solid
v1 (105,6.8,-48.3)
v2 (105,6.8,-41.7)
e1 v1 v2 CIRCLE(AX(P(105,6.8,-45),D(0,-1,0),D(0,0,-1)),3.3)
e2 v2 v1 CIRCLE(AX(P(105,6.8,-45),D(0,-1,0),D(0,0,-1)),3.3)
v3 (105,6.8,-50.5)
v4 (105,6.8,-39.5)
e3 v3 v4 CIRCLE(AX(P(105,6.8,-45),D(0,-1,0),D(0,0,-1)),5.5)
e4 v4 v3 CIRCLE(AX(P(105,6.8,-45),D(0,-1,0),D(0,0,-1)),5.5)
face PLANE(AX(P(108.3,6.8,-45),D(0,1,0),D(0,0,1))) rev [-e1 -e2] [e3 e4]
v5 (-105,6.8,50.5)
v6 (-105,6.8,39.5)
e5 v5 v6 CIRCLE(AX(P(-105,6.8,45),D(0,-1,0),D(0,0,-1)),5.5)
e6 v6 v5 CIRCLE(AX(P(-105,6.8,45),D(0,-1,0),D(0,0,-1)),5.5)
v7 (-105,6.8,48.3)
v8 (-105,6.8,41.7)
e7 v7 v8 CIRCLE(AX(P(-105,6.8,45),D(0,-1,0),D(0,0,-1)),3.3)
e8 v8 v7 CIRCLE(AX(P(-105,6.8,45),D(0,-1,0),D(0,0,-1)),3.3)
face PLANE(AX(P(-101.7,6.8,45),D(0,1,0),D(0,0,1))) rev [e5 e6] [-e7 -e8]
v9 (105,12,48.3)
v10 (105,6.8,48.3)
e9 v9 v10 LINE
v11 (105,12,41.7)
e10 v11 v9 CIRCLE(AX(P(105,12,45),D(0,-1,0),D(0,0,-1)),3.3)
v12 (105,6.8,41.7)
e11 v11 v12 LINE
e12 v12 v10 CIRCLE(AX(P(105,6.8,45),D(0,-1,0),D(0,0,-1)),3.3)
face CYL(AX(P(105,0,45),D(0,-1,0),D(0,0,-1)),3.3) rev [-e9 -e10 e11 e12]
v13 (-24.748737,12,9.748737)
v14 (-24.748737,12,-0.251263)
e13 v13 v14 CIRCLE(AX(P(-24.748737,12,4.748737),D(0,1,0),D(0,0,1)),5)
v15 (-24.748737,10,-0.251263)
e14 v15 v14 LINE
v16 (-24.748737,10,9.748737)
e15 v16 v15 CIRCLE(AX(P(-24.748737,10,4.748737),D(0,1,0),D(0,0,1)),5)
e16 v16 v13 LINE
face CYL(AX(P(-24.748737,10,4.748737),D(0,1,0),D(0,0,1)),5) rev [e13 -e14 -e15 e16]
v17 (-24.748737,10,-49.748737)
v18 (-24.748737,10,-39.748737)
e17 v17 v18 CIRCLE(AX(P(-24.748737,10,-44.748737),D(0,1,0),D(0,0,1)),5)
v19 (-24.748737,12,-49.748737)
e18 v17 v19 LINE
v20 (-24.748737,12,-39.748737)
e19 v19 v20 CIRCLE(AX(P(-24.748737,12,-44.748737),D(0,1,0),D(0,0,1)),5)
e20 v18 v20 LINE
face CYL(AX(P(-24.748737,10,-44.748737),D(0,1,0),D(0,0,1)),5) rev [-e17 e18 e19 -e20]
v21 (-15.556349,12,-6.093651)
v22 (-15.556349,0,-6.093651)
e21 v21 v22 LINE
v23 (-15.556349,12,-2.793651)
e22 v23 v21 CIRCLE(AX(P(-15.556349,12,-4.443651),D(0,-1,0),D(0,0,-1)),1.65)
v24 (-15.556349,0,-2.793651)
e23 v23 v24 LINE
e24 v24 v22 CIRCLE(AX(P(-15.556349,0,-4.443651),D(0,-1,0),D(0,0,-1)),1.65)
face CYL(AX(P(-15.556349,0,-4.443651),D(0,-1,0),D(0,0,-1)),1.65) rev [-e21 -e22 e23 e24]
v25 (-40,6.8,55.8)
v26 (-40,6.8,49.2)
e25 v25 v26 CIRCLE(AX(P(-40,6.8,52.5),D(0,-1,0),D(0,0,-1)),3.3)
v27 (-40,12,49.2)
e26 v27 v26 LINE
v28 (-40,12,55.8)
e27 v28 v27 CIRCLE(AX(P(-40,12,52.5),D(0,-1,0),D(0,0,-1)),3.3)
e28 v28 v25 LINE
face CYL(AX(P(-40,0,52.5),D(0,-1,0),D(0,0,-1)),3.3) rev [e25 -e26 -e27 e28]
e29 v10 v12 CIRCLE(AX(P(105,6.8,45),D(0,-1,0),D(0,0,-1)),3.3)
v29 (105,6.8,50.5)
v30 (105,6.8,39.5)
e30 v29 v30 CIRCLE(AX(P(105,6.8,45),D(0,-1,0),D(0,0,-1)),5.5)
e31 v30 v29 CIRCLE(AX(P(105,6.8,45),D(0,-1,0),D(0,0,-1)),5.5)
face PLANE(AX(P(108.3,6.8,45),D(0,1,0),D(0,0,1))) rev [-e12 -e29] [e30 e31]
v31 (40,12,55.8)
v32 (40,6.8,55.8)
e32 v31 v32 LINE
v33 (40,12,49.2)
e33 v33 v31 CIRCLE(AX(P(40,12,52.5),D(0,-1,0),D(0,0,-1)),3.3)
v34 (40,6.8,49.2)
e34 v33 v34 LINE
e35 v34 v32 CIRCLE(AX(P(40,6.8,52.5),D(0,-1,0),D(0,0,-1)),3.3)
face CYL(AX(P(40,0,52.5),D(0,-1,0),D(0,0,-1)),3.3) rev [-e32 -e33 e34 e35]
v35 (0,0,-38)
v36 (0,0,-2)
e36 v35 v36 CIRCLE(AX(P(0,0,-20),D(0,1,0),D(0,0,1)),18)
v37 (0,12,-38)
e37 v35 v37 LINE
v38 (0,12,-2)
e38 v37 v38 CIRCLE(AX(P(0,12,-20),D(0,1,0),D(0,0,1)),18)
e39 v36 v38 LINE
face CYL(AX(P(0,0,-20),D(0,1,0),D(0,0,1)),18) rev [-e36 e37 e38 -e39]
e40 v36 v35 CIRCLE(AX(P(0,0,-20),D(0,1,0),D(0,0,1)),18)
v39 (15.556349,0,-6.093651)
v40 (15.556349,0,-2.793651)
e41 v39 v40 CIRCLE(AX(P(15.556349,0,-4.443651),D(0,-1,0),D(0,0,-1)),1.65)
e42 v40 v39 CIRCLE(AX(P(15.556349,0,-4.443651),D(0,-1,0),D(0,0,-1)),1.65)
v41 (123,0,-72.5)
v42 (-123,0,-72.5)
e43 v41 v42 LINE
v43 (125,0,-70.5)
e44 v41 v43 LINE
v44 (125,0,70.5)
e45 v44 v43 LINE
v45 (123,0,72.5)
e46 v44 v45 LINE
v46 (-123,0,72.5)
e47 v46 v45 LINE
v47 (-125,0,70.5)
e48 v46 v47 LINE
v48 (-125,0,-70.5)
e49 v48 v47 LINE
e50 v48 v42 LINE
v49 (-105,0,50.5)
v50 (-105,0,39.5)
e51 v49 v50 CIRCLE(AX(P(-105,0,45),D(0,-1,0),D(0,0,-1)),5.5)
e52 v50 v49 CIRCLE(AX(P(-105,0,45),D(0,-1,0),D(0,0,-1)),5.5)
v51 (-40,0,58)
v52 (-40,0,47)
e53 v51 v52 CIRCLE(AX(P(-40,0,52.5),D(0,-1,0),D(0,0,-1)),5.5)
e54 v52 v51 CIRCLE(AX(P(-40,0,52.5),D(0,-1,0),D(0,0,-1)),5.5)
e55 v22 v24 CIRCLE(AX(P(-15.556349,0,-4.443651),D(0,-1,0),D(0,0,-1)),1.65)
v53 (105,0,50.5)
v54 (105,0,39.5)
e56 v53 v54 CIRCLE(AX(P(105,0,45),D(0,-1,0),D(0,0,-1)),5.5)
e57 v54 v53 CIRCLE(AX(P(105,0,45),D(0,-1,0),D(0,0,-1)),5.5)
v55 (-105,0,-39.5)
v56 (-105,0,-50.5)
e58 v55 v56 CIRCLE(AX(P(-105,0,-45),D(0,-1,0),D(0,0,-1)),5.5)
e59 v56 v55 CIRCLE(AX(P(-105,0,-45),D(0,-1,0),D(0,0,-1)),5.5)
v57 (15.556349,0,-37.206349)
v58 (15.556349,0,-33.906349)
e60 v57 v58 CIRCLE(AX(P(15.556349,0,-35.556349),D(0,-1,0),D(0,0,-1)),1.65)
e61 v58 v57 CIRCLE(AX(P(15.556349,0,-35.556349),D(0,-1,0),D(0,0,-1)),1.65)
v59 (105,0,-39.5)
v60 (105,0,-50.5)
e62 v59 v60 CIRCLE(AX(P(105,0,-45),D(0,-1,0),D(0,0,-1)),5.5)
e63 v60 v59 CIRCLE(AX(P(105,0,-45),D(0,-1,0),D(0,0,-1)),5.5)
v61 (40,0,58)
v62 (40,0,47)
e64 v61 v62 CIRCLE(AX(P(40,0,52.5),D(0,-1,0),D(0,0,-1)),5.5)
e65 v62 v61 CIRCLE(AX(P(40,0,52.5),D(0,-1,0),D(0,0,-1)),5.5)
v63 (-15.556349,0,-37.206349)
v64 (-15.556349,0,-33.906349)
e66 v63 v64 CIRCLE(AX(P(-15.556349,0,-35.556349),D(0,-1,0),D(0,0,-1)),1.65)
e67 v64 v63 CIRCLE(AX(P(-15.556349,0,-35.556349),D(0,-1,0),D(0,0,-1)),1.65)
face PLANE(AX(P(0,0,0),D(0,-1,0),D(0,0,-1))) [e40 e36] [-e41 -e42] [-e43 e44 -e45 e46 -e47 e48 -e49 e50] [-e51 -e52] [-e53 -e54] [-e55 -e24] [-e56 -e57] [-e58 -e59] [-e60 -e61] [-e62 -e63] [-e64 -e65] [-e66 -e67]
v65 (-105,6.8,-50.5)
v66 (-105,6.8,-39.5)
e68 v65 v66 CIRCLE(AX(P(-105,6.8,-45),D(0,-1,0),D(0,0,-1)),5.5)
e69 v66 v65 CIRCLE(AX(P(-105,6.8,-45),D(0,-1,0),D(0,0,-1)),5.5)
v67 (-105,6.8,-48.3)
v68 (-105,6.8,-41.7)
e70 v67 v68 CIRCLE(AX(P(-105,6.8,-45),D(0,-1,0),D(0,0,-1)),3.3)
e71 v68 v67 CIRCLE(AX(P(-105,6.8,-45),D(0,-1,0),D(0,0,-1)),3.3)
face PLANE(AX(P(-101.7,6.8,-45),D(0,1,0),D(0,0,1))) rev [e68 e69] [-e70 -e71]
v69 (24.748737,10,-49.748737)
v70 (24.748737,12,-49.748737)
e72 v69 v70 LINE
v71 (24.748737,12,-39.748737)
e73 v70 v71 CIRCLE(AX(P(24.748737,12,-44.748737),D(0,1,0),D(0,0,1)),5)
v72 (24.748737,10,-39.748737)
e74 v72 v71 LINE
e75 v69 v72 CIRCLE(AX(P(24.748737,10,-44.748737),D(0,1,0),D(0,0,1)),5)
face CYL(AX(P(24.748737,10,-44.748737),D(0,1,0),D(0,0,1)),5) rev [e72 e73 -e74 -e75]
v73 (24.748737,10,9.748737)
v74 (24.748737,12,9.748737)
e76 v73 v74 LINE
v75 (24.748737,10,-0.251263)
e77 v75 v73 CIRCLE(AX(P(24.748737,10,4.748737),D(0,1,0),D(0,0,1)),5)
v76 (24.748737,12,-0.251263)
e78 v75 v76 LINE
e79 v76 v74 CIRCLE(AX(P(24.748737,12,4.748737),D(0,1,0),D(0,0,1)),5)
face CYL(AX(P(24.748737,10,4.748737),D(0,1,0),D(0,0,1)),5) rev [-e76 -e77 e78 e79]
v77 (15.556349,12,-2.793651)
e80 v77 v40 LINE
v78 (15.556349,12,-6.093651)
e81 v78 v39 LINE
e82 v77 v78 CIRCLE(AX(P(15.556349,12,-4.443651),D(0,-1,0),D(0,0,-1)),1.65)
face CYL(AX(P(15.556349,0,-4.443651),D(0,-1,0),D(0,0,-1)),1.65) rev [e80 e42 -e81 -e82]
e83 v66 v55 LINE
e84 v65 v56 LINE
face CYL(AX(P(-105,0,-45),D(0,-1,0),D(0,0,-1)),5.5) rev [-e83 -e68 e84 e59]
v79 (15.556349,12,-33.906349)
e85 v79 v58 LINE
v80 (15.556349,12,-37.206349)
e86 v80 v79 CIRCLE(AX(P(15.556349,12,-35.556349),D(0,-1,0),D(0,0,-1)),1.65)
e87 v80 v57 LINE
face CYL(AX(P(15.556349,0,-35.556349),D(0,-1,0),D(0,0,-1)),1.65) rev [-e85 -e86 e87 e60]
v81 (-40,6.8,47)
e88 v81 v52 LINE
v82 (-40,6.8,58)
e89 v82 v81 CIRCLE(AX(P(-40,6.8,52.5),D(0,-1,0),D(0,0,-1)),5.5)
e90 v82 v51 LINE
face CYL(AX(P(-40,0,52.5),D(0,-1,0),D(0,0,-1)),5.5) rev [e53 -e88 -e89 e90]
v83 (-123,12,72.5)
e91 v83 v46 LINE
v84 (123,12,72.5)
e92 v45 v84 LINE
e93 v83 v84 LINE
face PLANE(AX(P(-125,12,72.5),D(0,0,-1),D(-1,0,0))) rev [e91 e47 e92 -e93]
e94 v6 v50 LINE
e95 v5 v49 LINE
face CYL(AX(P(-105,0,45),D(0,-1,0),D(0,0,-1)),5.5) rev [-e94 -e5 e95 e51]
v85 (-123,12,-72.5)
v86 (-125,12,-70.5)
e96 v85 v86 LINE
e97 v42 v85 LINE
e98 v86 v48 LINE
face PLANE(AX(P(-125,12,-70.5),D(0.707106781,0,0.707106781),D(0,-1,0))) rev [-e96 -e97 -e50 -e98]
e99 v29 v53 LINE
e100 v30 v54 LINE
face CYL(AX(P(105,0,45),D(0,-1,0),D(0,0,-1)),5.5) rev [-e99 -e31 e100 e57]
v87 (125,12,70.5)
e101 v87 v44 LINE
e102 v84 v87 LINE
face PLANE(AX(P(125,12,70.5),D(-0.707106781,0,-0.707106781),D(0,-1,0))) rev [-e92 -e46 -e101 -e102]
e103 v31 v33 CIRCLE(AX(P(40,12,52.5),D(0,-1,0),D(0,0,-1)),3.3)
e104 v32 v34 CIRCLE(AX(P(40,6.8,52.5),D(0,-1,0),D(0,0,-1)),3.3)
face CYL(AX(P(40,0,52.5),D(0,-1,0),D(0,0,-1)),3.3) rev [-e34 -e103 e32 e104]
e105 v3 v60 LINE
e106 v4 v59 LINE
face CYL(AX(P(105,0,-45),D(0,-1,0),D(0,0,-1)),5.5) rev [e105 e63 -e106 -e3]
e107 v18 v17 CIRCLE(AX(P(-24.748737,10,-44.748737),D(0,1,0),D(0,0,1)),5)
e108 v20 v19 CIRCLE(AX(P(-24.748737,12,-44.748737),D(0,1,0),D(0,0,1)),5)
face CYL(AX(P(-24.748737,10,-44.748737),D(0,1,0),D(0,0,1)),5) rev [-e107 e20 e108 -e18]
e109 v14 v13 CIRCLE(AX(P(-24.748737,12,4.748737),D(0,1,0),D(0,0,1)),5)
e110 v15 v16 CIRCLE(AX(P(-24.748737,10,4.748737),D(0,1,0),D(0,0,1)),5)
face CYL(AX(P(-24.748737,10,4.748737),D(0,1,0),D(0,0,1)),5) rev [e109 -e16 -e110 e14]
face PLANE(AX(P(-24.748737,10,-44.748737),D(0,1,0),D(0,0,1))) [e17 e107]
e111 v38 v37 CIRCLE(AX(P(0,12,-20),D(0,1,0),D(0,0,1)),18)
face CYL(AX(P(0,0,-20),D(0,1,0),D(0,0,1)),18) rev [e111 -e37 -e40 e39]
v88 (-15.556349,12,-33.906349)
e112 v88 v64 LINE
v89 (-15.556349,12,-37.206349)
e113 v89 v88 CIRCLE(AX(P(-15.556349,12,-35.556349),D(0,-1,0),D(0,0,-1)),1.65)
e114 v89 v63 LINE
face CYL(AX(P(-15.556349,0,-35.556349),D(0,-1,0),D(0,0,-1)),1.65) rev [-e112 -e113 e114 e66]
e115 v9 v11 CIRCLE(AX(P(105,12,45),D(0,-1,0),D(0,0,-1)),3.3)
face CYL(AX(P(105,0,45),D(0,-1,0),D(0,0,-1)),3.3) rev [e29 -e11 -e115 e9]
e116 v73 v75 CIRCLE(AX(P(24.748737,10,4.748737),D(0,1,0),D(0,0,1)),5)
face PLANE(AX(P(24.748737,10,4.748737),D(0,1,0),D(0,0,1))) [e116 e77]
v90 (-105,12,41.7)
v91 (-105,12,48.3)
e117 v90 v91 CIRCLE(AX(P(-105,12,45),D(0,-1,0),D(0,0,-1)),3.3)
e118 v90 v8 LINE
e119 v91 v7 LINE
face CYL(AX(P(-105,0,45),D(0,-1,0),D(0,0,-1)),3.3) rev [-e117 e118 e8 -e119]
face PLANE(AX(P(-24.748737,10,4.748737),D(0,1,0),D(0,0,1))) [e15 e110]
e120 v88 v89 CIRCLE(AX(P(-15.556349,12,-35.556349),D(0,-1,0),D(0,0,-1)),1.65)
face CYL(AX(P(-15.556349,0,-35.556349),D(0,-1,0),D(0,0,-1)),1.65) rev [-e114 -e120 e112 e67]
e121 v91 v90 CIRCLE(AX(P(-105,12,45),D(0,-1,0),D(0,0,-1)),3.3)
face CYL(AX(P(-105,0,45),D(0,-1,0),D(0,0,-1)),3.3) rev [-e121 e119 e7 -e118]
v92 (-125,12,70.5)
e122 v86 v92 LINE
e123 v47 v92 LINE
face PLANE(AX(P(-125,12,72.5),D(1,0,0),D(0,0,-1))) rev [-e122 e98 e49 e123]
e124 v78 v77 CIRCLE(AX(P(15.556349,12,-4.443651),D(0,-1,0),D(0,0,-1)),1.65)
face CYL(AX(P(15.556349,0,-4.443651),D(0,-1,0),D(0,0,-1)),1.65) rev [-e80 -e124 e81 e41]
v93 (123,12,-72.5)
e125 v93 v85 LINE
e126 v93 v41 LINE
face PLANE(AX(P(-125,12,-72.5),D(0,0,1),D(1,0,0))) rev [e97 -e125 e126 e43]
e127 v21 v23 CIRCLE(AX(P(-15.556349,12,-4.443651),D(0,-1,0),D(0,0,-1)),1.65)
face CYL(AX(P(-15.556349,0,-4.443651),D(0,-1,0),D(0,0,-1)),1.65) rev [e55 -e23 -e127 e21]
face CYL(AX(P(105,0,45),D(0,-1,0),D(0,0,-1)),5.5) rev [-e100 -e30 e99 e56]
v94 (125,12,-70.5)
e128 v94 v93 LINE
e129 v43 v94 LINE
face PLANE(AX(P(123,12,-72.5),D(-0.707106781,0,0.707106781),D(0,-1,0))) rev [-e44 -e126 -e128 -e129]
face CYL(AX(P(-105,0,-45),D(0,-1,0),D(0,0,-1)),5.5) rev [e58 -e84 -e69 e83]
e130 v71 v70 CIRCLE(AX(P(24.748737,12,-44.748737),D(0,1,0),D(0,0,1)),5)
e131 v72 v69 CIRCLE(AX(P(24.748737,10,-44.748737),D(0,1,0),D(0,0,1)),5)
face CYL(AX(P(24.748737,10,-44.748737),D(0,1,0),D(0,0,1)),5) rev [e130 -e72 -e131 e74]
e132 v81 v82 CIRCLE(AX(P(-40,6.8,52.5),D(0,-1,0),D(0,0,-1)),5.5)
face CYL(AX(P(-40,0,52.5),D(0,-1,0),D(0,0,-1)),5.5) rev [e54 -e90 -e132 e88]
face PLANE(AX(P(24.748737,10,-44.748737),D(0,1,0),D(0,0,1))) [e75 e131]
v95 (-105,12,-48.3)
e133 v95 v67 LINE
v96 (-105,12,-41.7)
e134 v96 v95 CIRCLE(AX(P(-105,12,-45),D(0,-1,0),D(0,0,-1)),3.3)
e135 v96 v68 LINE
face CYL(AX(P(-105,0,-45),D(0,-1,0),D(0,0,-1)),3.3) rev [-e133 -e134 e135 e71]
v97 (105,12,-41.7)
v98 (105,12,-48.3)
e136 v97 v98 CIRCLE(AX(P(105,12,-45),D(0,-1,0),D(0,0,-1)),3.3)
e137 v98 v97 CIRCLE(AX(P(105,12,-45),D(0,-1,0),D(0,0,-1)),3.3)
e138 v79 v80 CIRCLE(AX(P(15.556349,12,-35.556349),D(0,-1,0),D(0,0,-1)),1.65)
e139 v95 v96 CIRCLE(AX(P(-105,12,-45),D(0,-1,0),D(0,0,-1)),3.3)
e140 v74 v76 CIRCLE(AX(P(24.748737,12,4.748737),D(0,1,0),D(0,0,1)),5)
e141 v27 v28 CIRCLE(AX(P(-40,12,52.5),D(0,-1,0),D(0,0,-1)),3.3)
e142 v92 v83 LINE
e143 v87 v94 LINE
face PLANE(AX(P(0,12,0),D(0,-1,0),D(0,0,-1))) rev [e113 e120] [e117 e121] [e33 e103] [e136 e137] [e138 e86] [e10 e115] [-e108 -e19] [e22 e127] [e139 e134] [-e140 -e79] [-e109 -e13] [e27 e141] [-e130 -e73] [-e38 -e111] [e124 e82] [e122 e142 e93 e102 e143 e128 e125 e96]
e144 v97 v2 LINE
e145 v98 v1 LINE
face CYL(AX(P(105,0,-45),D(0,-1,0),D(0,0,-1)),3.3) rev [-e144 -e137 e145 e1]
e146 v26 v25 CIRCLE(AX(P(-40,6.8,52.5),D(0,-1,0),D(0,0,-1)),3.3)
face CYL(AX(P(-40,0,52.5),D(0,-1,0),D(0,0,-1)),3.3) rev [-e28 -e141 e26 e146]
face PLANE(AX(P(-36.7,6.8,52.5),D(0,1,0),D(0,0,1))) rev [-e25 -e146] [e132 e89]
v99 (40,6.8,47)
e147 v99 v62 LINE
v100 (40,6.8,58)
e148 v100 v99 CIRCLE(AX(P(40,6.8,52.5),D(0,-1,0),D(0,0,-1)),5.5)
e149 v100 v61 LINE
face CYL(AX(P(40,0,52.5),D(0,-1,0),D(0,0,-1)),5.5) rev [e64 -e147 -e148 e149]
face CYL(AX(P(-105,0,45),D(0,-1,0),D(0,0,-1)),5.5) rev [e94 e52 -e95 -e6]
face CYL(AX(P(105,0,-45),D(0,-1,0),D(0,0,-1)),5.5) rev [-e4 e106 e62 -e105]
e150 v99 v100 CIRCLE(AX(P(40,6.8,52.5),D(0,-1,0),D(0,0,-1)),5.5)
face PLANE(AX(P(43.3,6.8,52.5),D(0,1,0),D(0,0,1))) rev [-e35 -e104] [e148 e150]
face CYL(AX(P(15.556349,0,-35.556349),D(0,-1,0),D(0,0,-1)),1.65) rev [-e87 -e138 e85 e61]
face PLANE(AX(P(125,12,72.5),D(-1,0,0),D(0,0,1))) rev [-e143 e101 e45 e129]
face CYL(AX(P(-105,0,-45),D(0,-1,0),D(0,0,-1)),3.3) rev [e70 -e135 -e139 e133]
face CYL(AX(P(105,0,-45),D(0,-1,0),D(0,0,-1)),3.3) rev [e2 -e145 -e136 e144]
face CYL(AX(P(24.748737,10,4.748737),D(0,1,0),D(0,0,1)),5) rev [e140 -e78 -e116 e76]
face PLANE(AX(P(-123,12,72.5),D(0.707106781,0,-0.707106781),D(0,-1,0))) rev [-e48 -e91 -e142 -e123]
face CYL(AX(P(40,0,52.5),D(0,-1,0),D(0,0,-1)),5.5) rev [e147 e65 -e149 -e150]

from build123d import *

# Parameters (mm, degrees)
SKETCH_1_W                   = 250
SKETCH_1_H                   = 145
EXTRUDE_1_DEPTH              = 12
CHAMFER_1_SIZE               = 2
SKETCH_2_R                   = 18
CUT_EXTRUDE_1_DEPTH          = 146.000862066
HOLE_WIZARD_M4_1_D           = 3.3
HOLE_WIZARD_M6_1_D           = 6.6
HOLE_WIZARD_M6_1_CBORE_D     = 11
HOLE_WIZARD_M6_1_CBORE_DEPTH = 6.8
SKETCH_11_R                  = 5
CUT_EXTRUDE_2_DEPTH          = 2


with BuildPart() as part:
    # 草图1 → 凸台-拉伸1 (new body)
    with BuildSketch(Plane(origin=(0, 0, 0), x_dir=(1, 0, 0), z_dir=(0, 1, 0))):
        Rectangle(SKETCH_1_W, SKETCH_1_H)
    extrude(amount=EXTRUDE_1_DEPTH)

    # 倒角1
    chamfer_1_edges = [part.edges().sort_by_distance(p)[0] for p in [
        (125, 6, 72.5),
        (-125, 6, 72.5),
        (-125, 6, -72.5),
        (125, 6, -72.5),
    ]]
    chamfer(chamfer_1_edges, length=CHAMFER_1_SIZE)

    # 草图2 → 切除-拉伸1 (cut, through all)
    with BuildSketch(Plane(origin=(0, 12, 0), x_dir=(1, 0, 0), z_dir=(0, 1, 0))):
        with Locations(Location((0, 20, 0), (0, 0, 270))):
            Circle(SKETCH_2_R)
    extrude(amount=-CUT_EXTRUDE_1_DEPTH, mode=Mode.SUBTRACT)

    # M4 螺纹孔1 (through all)
    with Locations(Plane(origin=(0, 0, 0), x_dir=(-1, 0, 0), z_dir=(0, -1, 0))):
        with Locations((15.556349186, 35.556349186), (-15.556349186, 35.556349186), (-15.556349186, 4.443650814), (15.556349186, 4.443650814)):
            Hole(HOLE_WIZARD_M4_1_D / 2)

    # M6 六角圆柱头螺钉的柱形沉头孔1 (through all)
    with Locations(Plane(origin=(0, 0, 0), x_dir=(-1, 0, 0), z_dir=(0, -1, 0))):
        with Locations((-40, -52.5), (-105, 45), (-105, -45), (105, 45), (105, -45), (40, -52.5)):
            CounterBoreHole(HOLE_WIZARD_M6_1_D / 2, HOLE_WIZARD_M6_1_CBORE_D / 2, HOLE_WIZARD_M6_1_CBORE_DEPTH)

    # 草图11 → 切除-拉伸2 (cut)
    with BuildSketch(Plane(origin=(0, 12, 0), x_dir=(1, 0, 0), z_dir=(0, 1, 0))):
        with Locations(Location((24.748737342, -4.748737342, 0), (0, 0, 270))):
            Circle(SKETCH_11_R)
        with Locations(Location((-24.748737342, -4.748737342, 0), (0, 0, 270))):
            Circle(SKETCH_11_R)
        with Locations(Location((-24.748737342, 44.748737342, 0), (0, 0, 270))):
            Circle(SKETCH_11_R)
        with Locations(Location((24.748737342, 44.748737342, 0), (0, 0, 270))):
            Circle(SKETCH_11_R)
    extrude(amount=-CUT_EXTRUDE_2_DEPTH, mode=Mode.SUBTRACT)


solid = part.part
